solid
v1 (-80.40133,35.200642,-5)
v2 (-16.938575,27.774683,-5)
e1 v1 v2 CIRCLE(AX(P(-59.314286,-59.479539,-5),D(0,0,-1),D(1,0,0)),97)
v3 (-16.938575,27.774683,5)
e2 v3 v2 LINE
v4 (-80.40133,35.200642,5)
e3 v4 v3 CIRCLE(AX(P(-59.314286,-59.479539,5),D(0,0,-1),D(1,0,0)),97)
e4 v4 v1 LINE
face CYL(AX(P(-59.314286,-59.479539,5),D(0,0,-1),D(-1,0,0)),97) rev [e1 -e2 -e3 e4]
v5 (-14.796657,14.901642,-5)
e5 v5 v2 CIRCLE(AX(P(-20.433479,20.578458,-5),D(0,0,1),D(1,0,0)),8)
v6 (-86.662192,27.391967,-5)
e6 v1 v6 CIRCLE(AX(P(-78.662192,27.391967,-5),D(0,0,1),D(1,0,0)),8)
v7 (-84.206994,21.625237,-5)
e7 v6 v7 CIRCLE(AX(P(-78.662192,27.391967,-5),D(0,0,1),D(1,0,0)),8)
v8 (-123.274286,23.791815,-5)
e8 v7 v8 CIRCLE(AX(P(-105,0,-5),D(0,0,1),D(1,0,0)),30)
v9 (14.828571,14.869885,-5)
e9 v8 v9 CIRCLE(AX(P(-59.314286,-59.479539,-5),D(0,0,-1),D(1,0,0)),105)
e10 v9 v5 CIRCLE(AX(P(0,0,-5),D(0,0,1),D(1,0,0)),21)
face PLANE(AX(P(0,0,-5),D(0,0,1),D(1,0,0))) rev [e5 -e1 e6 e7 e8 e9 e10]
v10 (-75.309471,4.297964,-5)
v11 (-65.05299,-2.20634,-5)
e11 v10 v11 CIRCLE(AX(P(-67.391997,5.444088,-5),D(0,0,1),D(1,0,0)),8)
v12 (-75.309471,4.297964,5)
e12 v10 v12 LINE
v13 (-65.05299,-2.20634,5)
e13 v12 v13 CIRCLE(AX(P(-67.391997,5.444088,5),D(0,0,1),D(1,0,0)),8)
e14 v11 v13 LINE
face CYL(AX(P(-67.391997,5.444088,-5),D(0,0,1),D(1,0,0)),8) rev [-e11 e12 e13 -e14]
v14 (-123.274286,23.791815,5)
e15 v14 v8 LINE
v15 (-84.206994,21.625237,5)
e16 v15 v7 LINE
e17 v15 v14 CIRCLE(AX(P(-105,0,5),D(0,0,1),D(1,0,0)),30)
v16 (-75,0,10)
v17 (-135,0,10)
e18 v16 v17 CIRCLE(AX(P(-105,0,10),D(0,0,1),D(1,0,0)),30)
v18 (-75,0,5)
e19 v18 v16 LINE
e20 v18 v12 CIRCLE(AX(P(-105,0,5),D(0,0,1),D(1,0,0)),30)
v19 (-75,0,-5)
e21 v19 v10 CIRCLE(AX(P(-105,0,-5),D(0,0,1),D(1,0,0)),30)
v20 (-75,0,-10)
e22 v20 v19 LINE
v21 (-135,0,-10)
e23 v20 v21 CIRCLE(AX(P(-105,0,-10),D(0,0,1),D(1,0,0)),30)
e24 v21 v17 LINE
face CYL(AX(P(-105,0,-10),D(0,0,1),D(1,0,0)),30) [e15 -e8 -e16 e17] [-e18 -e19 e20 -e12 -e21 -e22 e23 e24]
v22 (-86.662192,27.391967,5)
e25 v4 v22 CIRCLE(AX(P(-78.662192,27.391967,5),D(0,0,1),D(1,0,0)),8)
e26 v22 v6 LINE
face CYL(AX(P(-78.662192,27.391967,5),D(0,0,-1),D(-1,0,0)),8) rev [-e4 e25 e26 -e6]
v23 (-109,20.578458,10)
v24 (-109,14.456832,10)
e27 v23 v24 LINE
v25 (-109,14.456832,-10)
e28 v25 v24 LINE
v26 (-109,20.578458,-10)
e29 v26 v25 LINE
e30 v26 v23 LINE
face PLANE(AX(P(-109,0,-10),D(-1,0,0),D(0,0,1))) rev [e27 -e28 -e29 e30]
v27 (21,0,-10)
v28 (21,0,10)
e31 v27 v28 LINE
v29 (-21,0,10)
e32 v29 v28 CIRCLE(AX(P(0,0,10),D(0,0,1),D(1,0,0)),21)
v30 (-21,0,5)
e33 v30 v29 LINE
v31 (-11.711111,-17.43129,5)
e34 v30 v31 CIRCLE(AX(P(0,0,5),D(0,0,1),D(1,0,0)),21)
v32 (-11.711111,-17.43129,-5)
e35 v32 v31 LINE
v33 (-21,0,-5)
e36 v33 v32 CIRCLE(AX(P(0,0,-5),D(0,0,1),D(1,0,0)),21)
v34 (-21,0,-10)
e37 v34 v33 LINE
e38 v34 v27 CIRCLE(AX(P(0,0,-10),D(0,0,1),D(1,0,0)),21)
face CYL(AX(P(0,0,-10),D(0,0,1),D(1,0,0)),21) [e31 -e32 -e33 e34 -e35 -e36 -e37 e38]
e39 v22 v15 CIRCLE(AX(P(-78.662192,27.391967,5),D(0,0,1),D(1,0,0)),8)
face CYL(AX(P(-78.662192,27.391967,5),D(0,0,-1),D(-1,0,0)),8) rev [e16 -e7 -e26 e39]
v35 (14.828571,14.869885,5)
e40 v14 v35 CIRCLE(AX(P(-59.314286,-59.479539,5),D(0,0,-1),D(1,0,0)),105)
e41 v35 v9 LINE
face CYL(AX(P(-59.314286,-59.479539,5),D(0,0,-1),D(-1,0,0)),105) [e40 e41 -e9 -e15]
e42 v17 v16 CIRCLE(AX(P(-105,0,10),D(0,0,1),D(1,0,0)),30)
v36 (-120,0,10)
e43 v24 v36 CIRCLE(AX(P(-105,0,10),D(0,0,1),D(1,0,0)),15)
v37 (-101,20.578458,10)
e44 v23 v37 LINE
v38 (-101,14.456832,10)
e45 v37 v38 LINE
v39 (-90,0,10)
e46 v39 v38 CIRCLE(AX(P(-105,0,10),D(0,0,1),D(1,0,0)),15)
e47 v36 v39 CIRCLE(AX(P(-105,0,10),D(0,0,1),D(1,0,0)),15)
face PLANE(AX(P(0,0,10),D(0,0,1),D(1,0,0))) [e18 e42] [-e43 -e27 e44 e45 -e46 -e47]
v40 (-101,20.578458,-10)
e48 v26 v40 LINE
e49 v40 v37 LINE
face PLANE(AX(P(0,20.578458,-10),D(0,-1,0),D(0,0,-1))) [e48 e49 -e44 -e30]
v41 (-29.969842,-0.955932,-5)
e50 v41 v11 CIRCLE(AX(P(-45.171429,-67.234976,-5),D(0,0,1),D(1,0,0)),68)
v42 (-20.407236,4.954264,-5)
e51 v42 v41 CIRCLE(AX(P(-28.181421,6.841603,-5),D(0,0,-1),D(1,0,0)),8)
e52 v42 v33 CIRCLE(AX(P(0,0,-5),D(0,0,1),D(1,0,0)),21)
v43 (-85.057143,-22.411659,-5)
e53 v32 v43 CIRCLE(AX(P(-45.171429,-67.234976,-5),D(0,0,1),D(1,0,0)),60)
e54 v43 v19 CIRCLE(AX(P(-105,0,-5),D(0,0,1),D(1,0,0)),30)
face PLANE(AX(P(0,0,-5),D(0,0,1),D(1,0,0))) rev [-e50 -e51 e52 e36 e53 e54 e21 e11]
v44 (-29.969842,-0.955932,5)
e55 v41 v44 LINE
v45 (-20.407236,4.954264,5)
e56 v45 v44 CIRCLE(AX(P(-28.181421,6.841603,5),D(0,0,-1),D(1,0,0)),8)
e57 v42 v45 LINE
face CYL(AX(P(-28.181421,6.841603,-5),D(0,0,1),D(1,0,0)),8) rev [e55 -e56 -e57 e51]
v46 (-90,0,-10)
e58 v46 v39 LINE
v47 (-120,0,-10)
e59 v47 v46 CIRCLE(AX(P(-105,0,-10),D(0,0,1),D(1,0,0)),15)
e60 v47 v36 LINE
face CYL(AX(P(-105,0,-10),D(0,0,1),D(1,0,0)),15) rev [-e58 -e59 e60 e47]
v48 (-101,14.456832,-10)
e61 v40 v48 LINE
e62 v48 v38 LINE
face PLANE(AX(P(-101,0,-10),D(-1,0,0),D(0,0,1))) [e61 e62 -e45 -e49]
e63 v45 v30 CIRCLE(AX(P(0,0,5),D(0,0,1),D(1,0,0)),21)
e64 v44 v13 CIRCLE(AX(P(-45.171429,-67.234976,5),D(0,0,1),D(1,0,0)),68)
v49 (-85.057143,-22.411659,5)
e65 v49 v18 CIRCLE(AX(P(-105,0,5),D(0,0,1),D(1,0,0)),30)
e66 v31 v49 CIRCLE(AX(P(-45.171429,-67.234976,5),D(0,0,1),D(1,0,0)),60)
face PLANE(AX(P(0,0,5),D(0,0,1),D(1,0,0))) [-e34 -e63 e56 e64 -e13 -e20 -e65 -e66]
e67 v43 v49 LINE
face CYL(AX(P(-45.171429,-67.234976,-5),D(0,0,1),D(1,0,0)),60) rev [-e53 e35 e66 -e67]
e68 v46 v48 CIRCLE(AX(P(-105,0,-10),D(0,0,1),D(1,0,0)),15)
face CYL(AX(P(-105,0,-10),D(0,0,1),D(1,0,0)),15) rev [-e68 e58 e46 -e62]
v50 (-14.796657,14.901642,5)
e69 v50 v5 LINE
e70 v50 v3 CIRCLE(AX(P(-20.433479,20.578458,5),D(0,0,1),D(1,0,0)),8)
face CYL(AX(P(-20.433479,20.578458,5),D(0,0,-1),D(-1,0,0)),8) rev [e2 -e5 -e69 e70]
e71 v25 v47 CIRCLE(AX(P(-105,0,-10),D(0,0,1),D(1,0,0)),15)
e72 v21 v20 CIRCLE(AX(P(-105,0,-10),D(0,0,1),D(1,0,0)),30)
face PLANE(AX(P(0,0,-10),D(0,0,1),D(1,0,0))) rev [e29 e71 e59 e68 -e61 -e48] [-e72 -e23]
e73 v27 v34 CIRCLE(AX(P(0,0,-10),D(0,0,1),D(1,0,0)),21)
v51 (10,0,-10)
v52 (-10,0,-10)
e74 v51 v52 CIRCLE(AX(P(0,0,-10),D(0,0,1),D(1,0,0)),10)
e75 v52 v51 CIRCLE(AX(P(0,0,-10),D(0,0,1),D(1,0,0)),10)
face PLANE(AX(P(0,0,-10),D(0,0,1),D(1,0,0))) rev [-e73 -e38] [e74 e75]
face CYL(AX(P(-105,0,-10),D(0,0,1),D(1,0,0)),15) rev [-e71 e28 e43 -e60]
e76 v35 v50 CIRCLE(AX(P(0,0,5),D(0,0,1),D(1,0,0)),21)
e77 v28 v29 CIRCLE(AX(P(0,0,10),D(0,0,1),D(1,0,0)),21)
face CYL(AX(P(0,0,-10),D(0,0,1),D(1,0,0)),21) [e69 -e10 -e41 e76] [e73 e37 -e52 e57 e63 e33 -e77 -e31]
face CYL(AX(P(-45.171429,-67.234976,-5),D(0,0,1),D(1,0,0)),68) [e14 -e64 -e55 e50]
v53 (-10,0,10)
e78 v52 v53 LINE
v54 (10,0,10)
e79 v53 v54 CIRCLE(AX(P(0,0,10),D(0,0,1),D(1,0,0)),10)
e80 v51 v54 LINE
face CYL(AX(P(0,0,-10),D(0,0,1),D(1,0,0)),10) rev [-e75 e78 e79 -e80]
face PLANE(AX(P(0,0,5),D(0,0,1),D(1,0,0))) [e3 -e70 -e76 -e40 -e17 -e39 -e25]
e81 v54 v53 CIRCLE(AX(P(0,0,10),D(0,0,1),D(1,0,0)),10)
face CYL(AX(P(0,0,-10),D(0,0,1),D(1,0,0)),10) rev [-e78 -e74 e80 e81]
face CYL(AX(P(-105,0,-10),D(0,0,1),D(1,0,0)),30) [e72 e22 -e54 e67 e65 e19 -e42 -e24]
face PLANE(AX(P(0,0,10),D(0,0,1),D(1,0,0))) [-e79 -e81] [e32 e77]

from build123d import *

# Parameters (mm, degrees)
HUB_BOSSES_20MM_DEPTH        = 10
HUB_BOSSES_20MM_DEPTH_BACK   = 10
HUB_BOSSES_20MM_2_DEPTH      = 10
HUB_BOSSES_20MM_2_DEPTH_BACK = 10
LEVER_PROFILE_SKETCH_R       = 10
ARM_WEB_10MM_DEPTH           = 5
ARM_WEB_10MM_DEPTH_BACK      = 5


with BuildPart() as part:
    # Lever Profile Sketch → Hub Bosses 20mm (new, two sides: drawn at the far end of the back side and taken through both)
    with BuildSketch(Plane.XY.offset(-HUB_BOSSES_20MM_DEPTH_BACK)):
        with BuildLine():
            ThreePointArc((-123.274285714, 23.791815434), (-128.116796704, -19.121027957), (-85.057142857, -22.411658773))
            ThreePointArc((-85.057142857, -22.411658773), (-77.629525814, -12.282391577), (-75, 0))
            ThreePointArc((-75, 0), (-75.077467799, 2.154545592), (-75.309471114, 4.297963991))
            ThreePointArc((-75.309471114, 4.297963991), (-78.312822706, 13.703815821), (-84.206993671, 21.625237289))
            ThreePointArc((-84.206993671, 21.625237289), (-103.338824634, 29.953972965), (-123.274285714, 23.791815434))
        make_face()
        with BuildLine():
            Line((-109, 14.456832295), (-109, 20.578458237))
            Line((-109, 20.578458237), (-101, 20.578458237))
            Line((-101, 20.578458237), (-101, 14.456832295))
            ThreePointArc((-101, 14.456832295), (-105, -15), (-109, 14.456832295))
        make_face(mode=Mode.SUBTRACT)
    extrude(amount=HUB_BOSSES_20MM_DEPTH + HUB_BOSSES_20MM_DEPTH_BACK)



with BuildPart() as body_2:
    # Lever Profile Sketch → Hub Bosses 20mm 2 (new, two sides: drawn at the far end of the back side and taken through both)
    with BuildSketch(Plane.XY.offset(-HUB_BOSSES_20MM_2_DEPTH_BACK)):
        with BuildLine():
            ThreePointArc((-20.407235595, 4.954264362), (-19.57486428, -7.604254627), (-11.711111111, -17.431290157))
            ThreePointArc((-11.711111111, -17.431290157), (9.875896584, -18.532853711), (21, 0))
            ThreePointArc((21, 0), (19.39587585, 8.049844719), (14.828571429, 14.869884646))
            ThreePointArc((14.828571429, 14.869884646), (0.022511477, 20.999987934), (-14.796657075, 14.901642172))
            ThreePointArc((-14.796657075, 14.901642172), (-18.291148026, 10.316680857), (-20.407235595, 4.954264362))
        make_face()
        Circle(LEVER_PROFILE_SKETCH_R, mode=Mode.SUBTRACT)
    extrude(amount=HUB_BOSSES_20MM_2_DEPTH + HUB_BOSSES_20MM_2_DEPTH_BACK)


with BuildPart() as part_1:
    add(part.part)

    add(body_2.part)  # Arm Web 10mm merges body 2
    # Sketch1_6 → Arm Web 10mm (add, two sides: drawn at the far end of the back side and taken through both)
    with BuildSketch(Plane.XY.offset(-ARM_WEB_10MM_DEPTH_BACK)):
        with BuildLine():
            ThreePointArc((-85.057142857, -22.411658773), (-49.236210113, -7.37282174), (-11.711111111, -17.431290157))
            ThreePointArc((-11.711111111, -17.431290157), (-19.57486428, -7.604254627), (-20.407235595, 4.954264362))
            ThreePointArc((-20.407235595, 4.954264362), (-23.975479097, 0.036453925), (-29.969842477, -0.955931516))
            ThreePointArc((-29.969842477, -0.955931516), (-47.593498278, 0.721874536), (-65.052989568, -2.206340072))
            ThreePointArc((-65.052989568, -2.206340072), (-71.676423998, -1.311923165), (-75.309471114, 4.297963991))
            ThreePointArc((-75.309471114, 4.297963991), (-75.077467799, 2.154545592), (-75, 0))
            ThreePointArc((-75, 0), (-77.629525814, -12.282391577), (-85.057142857, -22.411658773))
        make_face()
        with BuildLine():
            ThreePointArc((-14.796657075, 14.901642172), (0.022511477, 20.999987934), (14.828571429, 14.869884646))
            ThreePointArc((14.828571429, 14.869884646), (-52.545027473, 45.302030133), (-123.274285714, 23.791815434))
            ThreePointArc((-123.274285714, 23.791815434), (-103.338824634, 29.953972965), (-84.206993671, 21.625237289))
            ThreePointArc((-84.206993671, 21.625237289), (-86.365233313, 29.551401021), (-80.401329626, 35.200641913))
            ThreePointArc((-80.401329626, 35.200641913), (-48.040951998, 36.863141194), (-16.938574827, 27.77468267))
            ThreePointArc((-16.938574827, 27.77468267), (-12.541970936, 21.891509402), (-14.796657075, 14.901642172))
        make_face()
    extrude(amount=ARM_WEB_10MM_DEPTH + ARM_WEB_10MM_DEPTH_BACK)


solid = part_1.part
